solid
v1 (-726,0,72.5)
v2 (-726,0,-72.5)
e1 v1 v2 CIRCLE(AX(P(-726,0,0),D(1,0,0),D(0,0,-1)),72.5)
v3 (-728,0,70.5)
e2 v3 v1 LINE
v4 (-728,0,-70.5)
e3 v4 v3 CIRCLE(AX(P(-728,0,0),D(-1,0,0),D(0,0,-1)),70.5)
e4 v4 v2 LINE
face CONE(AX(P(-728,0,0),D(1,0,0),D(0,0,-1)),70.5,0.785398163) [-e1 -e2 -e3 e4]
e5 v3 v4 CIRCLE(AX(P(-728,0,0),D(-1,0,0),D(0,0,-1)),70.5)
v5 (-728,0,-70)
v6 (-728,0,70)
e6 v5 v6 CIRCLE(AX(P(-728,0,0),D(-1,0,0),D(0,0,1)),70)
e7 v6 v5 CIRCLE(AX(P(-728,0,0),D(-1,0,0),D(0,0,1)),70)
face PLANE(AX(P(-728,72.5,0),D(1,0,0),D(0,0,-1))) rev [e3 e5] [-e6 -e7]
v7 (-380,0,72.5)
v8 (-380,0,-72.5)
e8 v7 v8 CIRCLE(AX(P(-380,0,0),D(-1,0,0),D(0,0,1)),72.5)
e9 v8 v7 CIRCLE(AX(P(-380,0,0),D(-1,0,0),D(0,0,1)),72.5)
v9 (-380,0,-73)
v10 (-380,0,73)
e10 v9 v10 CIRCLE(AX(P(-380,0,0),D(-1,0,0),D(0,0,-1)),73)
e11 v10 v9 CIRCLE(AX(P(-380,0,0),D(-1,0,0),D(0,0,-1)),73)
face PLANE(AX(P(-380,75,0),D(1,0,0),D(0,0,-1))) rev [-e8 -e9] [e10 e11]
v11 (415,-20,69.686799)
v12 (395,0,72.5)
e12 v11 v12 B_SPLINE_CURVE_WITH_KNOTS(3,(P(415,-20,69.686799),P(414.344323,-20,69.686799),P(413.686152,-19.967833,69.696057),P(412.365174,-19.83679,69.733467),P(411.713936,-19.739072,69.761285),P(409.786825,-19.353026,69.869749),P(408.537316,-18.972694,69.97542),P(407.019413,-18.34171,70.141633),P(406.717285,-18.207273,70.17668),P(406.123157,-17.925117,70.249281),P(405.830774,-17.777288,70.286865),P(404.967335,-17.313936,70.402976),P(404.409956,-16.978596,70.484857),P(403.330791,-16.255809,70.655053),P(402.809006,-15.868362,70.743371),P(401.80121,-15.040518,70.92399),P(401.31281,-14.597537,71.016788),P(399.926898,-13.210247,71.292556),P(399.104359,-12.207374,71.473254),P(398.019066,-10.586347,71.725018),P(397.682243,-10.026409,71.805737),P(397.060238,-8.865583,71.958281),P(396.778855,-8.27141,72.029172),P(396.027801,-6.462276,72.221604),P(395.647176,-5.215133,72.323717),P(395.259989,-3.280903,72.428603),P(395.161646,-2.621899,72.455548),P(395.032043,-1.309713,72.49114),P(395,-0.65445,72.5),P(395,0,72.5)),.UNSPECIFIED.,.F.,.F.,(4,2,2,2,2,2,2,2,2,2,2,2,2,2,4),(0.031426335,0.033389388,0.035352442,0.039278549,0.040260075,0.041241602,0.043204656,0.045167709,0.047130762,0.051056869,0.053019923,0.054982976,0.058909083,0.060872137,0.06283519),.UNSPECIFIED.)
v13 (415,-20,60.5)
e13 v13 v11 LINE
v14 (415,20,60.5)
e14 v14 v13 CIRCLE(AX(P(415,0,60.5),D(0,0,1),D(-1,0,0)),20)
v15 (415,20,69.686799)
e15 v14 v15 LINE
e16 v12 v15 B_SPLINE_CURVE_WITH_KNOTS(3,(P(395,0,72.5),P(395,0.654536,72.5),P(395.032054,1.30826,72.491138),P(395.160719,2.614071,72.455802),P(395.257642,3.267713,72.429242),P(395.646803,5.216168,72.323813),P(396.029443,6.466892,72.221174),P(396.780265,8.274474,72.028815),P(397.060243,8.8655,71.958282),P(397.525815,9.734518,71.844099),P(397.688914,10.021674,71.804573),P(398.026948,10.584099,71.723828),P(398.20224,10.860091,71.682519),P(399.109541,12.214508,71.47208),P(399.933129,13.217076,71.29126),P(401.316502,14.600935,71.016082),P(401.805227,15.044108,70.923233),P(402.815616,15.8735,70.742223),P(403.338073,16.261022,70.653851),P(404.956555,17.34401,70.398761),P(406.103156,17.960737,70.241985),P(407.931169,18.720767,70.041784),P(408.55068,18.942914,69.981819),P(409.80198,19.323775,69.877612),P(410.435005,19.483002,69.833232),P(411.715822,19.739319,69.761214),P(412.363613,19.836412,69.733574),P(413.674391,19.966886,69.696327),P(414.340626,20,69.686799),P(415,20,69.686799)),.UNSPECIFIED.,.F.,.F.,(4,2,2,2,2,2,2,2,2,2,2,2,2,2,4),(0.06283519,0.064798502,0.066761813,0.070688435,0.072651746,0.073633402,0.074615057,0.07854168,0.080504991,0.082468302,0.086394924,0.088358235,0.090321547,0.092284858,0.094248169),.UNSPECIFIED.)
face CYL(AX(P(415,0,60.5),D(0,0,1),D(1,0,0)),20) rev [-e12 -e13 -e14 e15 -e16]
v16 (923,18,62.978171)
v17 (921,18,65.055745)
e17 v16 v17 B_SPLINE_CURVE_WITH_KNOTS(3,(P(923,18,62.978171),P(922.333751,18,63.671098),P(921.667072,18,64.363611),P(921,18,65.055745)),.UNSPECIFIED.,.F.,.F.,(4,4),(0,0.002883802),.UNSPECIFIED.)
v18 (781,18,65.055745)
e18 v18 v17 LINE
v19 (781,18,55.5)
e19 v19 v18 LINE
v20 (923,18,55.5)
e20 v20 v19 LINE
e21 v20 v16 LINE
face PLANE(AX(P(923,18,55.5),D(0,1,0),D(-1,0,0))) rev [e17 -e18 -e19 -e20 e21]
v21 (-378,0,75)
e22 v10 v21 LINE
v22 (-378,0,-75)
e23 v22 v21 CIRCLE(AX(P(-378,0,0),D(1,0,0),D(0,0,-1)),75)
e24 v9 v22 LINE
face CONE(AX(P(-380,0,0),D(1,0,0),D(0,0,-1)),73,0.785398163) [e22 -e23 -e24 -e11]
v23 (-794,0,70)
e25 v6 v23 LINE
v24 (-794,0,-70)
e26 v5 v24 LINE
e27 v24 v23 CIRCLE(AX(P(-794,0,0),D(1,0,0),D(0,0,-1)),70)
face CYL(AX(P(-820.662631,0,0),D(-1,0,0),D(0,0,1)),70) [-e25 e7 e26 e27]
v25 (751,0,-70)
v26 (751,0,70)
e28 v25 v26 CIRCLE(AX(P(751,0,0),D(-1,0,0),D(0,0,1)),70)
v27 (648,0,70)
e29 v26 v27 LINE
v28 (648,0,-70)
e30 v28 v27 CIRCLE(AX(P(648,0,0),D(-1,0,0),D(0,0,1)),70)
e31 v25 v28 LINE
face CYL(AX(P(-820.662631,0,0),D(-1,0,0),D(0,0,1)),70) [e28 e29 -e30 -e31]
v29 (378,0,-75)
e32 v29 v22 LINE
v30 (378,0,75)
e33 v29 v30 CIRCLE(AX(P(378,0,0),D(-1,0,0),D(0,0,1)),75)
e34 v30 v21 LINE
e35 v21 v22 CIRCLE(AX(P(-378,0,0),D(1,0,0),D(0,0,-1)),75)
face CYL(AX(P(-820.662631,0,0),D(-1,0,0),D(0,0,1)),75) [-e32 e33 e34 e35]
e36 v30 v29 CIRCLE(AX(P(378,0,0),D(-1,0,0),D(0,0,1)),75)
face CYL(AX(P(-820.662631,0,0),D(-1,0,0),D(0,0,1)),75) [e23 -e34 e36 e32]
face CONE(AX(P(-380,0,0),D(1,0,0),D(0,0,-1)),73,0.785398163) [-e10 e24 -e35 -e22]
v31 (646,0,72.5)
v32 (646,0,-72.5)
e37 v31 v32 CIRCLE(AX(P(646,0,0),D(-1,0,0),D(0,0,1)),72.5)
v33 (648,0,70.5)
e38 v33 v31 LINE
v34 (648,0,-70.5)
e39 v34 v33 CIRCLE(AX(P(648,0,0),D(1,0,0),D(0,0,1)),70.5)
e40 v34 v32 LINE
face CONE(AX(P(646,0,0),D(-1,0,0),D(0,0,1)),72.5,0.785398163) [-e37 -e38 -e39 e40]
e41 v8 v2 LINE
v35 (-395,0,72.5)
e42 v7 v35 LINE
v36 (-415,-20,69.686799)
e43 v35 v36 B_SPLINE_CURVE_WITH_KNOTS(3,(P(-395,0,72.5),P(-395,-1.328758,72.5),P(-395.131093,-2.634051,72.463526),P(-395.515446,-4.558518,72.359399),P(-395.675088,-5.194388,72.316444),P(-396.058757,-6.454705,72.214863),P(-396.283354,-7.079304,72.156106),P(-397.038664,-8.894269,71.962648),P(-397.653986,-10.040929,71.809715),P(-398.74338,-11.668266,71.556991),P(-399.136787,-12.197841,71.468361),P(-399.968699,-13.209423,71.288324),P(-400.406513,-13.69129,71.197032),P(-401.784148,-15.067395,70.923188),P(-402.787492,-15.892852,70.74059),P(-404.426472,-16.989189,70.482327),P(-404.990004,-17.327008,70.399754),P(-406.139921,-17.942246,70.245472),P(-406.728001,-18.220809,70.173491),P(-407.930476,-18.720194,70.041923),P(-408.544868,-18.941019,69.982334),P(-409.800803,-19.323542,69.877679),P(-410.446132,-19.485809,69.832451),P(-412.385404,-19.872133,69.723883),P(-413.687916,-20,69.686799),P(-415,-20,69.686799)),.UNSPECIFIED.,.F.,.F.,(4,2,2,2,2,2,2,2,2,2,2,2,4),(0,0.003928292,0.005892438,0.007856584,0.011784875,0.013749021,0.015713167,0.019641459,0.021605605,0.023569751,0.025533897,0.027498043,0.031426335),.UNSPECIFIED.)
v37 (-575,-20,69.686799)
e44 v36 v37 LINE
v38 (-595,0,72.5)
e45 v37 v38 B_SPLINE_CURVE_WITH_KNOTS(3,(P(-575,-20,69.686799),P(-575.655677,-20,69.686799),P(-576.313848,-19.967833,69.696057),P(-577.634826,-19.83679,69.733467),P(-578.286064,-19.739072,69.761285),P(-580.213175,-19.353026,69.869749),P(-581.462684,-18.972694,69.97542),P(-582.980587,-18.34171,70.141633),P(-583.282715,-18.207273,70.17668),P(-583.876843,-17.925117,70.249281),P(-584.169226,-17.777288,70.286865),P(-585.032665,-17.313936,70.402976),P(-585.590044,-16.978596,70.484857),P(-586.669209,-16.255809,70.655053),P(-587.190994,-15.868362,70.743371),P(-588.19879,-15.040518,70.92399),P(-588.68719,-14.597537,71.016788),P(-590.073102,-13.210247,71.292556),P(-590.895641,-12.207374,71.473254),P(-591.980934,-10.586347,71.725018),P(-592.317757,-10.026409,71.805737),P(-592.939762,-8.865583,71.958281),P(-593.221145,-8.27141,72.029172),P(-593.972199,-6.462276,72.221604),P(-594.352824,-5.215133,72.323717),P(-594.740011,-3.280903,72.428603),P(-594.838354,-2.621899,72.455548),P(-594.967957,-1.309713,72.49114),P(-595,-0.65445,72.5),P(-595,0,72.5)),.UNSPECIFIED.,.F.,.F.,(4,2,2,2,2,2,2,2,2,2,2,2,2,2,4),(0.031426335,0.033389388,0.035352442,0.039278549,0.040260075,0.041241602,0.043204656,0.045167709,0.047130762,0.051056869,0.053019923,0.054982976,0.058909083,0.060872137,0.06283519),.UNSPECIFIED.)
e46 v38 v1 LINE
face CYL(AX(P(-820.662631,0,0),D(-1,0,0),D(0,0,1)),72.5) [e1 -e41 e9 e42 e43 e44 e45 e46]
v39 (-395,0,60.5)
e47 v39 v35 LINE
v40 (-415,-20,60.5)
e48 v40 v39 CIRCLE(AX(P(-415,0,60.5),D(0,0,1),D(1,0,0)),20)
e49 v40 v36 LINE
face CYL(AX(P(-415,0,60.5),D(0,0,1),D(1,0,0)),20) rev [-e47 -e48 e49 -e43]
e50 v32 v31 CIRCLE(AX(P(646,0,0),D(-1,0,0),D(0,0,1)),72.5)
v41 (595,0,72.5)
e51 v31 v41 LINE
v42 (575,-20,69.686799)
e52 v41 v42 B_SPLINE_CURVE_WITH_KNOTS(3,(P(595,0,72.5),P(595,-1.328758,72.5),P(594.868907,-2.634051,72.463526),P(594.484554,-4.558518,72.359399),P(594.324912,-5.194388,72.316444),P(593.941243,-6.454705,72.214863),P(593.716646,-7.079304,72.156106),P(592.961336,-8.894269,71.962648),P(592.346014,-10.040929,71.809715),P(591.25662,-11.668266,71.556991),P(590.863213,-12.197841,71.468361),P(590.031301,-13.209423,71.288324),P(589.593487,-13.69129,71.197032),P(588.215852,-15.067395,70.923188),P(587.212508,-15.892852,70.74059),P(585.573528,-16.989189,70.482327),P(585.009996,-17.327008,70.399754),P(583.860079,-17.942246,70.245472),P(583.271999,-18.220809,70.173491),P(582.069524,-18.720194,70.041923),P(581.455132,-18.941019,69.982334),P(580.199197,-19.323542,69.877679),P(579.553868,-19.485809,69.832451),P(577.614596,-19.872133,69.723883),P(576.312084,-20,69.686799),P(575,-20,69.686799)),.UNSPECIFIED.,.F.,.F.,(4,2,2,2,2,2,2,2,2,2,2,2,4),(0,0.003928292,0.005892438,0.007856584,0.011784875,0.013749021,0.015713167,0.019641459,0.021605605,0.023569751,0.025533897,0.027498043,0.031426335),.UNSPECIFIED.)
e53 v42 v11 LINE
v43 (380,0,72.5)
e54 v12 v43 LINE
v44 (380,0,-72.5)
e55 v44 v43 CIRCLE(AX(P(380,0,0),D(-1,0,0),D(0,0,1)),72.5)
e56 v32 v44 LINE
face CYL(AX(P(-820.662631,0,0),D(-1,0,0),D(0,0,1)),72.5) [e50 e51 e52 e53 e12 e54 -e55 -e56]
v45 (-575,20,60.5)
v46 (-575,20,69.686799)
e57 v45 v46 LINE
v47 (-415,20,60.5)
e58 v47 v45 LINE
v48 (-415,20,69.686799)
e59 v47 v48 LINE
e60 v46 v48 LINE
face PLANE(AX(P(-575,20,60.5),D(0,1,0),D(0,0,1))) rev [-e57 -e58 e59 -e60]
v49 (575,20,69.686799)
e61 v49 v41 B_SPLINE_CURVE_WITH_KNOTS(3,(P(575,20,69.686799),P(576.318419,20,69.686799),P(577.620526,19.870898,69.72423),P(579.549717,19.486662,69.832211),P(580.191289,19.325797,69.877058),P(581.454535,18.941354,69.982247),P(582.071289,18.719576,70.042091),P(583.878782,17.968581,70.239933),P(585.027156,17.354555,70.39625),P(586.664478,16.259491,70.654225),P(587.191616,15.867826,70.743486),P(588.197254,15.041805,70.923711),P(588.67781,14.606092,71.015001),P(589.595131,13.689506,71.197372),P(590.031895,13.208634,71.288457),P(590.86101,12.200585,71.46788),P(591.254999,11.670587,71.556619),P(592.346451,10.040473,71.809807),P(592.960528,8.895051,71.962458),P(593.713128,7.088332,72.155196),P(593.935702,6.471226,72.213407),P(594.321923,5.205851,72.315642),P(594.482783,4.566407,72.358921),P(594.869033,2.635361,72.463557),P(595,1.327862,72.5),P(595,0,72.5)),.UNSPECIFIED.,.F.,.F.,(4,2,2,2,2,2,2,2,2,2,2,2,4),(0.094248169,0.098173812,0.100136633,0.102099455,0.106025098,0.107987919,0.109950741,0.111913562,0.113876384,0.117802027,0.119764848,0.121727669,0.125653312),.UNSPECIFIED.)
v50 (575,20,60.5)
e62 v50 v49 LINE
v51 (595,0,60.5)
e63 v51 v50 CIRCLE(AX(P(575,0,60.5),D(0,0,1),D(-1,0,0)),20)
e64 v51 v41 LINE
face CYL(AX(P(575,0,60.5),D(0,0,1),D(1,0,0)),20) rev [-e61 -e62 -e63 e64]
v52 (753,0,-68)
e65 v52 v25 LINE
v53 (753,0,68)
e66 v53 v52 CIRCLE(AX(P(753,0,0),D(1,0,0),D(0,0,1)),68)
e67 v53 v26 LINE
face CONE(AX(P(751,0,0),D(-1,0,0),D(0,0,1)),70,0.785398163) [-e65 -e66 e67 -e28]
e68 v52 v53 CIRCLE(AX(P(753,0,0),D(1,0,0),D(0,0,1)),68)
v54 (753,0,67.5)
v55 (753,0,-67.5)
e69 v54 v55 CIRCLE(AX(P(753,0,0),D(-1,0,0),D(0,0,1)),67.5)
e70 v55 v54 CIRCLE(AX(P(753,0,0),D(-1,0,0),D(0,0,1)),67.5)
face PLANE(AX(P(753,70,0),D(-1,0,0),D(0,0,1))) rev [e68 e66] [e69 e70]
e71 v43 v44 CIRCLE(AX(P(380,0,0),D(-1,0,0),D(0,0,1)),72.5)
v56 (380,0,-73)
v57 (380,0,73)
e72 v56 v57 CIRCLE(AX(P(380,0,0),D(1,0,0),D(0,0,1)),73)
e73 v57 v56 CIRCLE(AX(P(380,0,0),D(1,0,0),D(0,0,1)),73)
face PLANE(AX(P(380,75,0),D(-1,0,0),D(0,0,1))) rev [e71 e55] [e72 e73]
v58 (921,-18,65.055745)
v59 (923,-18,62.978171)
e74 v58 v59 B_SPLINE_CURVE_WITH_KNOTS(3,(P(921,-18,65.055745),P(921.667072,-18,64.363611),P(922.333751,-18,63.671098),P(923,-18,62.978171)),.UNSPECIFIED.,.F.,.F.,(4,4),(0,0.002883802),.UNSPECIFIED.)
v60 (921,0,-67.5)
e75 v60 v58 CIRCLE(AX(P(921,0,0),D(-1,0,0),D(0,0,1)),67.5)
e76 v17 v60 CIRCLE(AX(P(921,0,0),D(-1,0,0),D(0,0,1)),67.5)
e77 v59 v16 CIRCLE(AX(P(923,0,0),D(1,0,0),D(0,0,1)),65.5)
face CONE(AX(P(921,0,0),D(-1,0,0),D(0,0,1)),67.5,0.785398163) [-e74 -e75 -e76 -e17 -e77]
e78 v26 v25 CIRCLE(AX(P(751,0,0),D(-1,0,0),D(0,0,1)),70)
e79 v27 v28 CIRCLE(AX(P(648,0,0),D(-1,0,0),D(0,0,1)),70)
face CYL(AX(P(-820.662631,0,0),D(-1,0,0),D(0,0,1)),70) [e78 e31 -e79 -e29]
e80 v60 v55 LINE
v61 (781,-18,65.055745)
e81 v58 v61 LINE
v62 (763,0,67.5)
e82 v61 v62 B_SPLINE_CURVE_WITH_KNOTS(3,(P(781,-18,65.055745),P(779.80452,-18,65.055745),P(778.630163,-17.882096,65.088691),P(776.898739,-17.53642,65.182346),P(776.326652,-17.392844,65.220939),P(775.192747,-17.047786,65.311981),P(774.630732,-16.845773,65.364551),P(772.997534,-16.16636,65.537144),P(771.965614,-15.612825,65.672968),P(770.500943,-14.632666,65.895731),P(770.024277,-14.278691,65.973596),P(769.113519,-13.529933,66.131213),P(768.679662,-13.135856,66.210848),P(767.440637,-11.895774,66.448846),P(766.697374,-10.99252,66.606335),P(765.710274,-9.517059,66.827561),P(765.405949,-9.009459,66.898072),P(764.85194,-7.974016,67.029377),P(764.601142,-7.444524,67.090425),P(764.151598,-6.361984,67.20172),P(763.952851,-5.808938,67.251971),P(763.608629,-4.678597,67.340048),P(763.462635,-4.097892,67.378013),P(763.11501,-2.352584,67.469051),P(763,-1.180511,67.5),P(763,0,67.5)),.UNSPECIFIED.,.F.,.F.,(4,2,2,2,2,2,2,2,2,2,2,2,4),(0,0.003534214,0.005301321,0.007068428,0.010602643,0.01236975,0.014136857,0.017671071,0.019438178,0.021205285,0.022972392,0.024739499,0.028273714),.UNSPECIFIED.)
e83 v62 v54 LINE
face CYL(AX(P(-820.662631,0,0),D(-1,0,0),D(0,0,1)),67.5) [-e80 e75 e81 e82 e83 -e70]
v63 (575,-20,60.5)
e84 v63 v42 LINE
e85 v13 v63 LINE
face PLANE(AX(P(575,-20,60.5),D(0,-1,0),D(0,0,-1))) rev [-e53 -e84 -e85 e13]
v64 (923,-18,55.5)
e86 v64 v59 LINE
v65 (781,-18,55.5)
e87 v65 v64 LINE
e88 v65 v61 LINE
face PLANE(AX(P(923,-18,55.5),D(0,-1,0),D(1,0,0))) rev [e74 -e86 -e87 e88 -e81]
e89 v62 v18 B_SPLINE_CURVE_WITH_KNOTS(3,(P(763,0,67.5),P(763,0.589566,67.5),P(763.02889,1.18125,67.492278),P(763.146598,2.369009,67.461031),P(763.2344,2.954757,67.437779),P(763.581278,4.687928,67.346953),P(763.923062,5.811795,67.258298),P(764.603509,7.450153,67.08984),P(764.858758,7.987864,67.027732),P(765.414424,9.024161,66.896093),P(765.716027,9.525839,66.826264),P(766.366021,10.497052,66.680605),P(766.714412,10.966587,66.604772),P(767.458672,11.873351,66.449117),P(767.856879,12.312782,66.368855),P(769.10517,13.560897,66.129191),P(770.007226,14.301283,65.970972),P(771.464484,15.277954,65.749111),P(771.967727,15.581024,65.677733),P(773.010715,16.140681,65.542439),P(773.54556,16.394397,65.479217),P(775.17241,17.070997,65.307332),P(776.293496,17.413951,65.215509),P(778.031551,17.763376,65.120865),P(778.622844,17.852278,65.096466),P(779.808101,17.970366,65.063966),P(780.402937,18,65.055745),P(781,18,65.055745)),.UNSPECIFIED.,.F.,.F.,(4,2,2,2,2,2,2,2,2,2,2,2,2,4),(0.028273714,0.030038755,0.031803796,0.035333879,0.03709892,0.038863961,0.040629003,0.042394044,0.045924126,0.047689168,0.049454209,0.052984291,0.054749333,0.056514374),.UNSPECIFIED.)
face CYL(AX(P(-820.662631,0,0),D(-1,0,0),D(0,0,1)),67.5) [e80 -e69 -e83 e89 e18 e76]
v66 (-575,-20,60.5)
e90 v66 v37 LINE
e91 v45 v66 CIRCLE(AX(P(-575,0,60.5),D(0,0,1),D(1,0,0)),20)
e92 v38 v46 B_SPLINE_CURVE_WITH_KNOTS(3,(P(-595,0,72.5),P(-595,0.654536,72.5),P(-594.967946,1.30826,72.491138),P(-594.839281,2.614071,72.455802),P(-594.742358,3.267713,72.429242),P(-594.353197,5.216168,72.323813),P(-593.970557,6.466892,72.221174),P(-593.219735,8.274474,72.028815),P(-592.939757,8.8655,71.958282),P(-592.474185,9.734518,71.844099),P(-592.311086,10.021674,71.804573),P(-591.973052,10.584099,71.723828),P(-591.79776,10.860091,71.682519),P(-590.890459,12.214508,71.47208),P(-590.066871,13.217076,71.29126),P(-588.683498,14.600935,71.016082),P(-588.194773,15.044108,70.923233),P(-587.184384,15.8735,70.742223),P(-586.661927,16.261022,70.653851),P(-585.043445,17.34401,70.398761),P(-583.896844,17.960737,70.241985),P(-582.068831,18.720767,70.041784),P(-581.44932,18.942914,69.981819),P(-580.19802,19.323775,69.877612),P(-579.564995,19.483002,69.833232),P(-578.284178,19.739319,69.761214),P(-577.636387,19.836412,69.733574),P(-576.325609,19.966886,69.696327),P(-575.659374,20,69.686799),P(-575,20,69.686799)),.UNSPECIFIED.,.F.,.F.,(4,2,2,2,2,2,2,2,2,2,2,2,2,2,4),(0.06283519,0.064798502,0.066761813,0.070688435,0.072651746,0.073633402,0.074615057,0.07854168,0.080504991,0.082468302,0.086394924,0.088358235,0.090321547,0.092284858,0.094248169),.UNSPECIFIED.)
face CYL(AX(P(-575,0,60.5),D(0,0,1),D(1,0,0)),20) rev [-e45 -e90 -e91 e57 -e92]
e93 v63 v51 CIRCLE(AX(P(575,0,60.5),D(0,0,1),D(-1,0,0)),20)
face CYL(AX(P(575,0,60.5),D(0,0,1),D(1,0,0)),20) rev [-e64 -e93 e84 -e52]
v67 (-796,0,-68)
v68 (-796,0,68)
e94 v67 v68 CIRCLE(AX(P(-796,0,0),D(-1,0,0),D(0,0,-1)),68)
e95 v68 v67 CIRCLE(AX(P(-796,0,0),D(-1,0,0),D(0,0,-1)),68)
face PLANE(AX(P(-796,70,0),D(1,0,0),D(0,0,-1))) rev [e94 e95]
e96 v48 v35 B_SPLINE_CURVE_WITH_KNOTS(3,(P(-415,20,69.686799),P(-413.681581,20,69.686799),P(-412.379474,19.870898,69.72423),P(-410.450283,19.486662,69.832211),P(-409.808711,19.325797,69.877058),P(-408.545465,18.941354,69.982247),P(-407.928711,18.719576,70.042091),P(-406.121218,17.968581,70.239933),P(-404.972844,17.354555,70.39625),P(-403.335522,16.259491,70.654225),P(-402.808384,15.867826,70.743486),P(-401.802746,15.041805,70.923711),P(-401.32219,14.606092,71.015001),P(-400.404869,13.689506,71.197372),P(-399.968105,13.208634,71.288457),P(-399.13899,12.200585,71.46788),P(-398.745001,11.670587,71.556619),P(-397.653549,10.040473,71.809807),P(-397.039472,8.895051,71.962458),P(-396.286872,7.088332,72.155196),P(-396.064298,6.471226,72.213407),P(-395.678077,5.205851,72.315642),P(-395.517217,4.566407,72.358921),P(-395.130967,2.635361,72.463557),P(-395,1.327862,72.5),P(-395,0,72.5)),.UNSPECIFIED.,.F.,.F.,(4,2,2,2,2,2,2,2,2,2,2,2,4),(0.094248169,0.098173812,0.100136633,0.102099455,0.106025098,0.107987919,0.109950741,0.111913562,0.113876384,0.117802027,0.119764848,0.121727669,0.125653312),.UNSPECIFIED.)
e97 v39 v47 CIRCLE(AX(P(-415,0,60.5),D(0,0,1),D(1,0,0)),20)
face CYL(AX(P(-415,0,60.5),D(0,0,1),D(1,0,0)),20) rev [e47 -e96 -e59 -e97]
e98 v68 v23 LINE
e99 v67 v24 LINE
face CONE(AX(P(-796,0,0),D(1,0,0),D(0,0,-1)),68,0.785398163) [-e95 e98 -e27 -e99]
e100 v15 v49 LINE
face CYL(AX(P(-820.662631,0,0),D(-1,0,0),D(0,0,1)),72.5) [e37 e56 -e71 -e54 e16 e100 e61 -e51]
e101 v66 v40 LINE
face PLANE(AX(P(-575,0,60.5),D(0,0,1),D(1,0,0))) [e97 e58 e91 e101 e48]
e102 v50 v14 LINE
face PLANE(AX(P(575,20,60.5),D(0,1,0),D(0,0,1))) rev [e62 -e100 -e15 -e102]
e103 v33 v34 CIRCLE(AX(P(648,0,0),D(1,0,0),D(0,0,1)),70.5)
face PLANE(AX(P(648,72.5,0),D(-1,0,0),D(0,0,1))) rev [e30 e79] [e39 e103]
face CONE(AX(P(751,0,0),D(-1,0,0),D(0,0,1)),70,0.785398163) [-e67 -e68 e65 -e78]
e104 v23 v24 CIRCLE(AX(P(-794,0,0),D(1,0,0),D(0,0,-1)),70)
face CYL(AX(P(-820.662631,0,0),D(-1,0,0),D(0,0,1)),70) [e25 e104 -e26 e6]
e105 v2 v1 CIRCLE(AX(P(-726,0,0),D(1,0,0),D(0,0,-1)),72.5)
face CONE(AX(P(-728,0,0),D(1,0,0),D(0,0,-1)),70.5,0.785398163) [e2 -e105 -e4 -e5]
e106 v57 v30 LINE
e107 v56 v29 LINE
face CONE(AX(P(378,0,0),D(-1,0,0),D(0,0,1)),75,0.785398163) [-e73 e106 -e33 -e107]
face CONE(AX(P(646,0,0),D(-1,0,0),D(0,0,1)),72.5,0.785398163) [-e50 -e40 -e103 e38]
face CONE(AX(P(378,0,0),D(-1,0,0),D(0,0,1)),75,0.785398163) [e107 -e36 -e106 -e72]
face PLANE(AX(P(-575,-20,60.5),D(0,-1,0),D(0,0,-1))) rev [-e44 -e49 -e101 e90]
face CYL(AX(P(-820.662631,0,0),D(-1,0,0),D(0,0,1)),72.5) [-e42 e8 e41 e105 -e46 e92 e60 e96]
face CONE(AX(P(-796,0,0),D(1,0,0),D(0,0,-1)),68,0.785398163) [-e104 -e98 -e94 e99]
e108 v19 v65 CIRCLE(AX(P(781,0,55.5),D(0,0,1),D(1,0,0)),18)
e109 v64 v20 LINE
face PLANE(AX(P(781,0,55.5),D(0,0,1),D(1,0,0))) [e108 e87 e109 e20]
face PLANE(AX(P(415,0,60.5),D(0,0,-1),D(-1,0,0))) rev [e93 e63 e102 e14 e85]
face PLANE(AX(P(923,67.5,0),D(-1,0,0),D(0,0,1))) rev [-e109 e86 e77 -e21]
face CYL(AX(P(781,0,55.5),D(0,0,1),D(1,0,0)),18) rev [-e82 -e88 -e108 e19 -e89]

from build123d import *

# Parameters (mm, degrees)
CUT_EXTRUDE1_DEPTH = 12
CUT_EXTRUDE2_DEPTH = 12
CHAMFER1_SIZE      = 2


with BuildPart() as part:
    # Sketch1 → Revolve1 (revolve)
    with BuildSketch(Plane.XY, mode=Mode.PRIVATE) as revolve1_sk:
        Polygon((-796, 70), (-728, 70), (-728, 72.5), (-380, 72.5), (-380, 75), (380, 75), (380, 72.5), (648, 72.5), (648, 70), (753, 70), (753, 67.5), (923, 67.5), (923, 0), (-796, 0), align=None)
    revolve(revolve1_sk.sketch.rotate(Axis((-820.662631097, 0, 0), (1, 0, 0)), 90), axis=Axis((-820.662631097, 0, 0), (1, 0, 0)))

    # Sketch2 → Cut-Extrude1 (cut)
    with BuildSketch(Plane.XY.offset(67.5)):
        with BuildLine():
            Line((923, -18), (781, -18))
            ThreePointArc((781, -18), (763, 0), (781, 18))
            Line((781, 18), (923, 18))
            Line((923, 18), (923, 0))
            Line((923, 0), (923, -18))
        make_face()
    extrude(amount=-CUT_EXTRUDE1_DEPTH, mode=Mode.SUBTRACT)

    # Sketch3 → Cut-Extrude2 (cut)
    with BuildSketch(Plane.XY.offset(72.5)):
        with BuildLine():
            Line((-575, -20), (-415, -20))
            ThreePointArc((-415, -20), (-395, 0), (-415, 20))
            Line((-415, 20), (-575, 20))
            ThreePointArc((-575, 20), (-595, 0), (-575, -20))
        make_face()
        with BuildLine():
            Line((575, 20), (415, 20))
            ThreePointArc((415, 20), (395, 0), (415, -20))
            Line((415, -20), (575, -20))
            ThreePointArc((575, -20), (595, 0), (575, 20))
        make_face()
    extrude(amount=-CUT_EXTRUDE2_DEPTH, mode=Mode.SUBTRACT)

    # Chamfer1
    chamfer1_edges = [part.edges().sort_by_distance(p)[0] for p in [
        (-796, 0, -70),
        (-728, 0, -72.5),
        (-380, 0, -75),
        (380, 0, -75),
        (648, 0, -72.5),
        (753, 0, -70),
        (923, 0, -67.5),
    ]]
    chamfer(chamfer1_edges, length=CHAMFER1_SIZE)


solid = part.part
